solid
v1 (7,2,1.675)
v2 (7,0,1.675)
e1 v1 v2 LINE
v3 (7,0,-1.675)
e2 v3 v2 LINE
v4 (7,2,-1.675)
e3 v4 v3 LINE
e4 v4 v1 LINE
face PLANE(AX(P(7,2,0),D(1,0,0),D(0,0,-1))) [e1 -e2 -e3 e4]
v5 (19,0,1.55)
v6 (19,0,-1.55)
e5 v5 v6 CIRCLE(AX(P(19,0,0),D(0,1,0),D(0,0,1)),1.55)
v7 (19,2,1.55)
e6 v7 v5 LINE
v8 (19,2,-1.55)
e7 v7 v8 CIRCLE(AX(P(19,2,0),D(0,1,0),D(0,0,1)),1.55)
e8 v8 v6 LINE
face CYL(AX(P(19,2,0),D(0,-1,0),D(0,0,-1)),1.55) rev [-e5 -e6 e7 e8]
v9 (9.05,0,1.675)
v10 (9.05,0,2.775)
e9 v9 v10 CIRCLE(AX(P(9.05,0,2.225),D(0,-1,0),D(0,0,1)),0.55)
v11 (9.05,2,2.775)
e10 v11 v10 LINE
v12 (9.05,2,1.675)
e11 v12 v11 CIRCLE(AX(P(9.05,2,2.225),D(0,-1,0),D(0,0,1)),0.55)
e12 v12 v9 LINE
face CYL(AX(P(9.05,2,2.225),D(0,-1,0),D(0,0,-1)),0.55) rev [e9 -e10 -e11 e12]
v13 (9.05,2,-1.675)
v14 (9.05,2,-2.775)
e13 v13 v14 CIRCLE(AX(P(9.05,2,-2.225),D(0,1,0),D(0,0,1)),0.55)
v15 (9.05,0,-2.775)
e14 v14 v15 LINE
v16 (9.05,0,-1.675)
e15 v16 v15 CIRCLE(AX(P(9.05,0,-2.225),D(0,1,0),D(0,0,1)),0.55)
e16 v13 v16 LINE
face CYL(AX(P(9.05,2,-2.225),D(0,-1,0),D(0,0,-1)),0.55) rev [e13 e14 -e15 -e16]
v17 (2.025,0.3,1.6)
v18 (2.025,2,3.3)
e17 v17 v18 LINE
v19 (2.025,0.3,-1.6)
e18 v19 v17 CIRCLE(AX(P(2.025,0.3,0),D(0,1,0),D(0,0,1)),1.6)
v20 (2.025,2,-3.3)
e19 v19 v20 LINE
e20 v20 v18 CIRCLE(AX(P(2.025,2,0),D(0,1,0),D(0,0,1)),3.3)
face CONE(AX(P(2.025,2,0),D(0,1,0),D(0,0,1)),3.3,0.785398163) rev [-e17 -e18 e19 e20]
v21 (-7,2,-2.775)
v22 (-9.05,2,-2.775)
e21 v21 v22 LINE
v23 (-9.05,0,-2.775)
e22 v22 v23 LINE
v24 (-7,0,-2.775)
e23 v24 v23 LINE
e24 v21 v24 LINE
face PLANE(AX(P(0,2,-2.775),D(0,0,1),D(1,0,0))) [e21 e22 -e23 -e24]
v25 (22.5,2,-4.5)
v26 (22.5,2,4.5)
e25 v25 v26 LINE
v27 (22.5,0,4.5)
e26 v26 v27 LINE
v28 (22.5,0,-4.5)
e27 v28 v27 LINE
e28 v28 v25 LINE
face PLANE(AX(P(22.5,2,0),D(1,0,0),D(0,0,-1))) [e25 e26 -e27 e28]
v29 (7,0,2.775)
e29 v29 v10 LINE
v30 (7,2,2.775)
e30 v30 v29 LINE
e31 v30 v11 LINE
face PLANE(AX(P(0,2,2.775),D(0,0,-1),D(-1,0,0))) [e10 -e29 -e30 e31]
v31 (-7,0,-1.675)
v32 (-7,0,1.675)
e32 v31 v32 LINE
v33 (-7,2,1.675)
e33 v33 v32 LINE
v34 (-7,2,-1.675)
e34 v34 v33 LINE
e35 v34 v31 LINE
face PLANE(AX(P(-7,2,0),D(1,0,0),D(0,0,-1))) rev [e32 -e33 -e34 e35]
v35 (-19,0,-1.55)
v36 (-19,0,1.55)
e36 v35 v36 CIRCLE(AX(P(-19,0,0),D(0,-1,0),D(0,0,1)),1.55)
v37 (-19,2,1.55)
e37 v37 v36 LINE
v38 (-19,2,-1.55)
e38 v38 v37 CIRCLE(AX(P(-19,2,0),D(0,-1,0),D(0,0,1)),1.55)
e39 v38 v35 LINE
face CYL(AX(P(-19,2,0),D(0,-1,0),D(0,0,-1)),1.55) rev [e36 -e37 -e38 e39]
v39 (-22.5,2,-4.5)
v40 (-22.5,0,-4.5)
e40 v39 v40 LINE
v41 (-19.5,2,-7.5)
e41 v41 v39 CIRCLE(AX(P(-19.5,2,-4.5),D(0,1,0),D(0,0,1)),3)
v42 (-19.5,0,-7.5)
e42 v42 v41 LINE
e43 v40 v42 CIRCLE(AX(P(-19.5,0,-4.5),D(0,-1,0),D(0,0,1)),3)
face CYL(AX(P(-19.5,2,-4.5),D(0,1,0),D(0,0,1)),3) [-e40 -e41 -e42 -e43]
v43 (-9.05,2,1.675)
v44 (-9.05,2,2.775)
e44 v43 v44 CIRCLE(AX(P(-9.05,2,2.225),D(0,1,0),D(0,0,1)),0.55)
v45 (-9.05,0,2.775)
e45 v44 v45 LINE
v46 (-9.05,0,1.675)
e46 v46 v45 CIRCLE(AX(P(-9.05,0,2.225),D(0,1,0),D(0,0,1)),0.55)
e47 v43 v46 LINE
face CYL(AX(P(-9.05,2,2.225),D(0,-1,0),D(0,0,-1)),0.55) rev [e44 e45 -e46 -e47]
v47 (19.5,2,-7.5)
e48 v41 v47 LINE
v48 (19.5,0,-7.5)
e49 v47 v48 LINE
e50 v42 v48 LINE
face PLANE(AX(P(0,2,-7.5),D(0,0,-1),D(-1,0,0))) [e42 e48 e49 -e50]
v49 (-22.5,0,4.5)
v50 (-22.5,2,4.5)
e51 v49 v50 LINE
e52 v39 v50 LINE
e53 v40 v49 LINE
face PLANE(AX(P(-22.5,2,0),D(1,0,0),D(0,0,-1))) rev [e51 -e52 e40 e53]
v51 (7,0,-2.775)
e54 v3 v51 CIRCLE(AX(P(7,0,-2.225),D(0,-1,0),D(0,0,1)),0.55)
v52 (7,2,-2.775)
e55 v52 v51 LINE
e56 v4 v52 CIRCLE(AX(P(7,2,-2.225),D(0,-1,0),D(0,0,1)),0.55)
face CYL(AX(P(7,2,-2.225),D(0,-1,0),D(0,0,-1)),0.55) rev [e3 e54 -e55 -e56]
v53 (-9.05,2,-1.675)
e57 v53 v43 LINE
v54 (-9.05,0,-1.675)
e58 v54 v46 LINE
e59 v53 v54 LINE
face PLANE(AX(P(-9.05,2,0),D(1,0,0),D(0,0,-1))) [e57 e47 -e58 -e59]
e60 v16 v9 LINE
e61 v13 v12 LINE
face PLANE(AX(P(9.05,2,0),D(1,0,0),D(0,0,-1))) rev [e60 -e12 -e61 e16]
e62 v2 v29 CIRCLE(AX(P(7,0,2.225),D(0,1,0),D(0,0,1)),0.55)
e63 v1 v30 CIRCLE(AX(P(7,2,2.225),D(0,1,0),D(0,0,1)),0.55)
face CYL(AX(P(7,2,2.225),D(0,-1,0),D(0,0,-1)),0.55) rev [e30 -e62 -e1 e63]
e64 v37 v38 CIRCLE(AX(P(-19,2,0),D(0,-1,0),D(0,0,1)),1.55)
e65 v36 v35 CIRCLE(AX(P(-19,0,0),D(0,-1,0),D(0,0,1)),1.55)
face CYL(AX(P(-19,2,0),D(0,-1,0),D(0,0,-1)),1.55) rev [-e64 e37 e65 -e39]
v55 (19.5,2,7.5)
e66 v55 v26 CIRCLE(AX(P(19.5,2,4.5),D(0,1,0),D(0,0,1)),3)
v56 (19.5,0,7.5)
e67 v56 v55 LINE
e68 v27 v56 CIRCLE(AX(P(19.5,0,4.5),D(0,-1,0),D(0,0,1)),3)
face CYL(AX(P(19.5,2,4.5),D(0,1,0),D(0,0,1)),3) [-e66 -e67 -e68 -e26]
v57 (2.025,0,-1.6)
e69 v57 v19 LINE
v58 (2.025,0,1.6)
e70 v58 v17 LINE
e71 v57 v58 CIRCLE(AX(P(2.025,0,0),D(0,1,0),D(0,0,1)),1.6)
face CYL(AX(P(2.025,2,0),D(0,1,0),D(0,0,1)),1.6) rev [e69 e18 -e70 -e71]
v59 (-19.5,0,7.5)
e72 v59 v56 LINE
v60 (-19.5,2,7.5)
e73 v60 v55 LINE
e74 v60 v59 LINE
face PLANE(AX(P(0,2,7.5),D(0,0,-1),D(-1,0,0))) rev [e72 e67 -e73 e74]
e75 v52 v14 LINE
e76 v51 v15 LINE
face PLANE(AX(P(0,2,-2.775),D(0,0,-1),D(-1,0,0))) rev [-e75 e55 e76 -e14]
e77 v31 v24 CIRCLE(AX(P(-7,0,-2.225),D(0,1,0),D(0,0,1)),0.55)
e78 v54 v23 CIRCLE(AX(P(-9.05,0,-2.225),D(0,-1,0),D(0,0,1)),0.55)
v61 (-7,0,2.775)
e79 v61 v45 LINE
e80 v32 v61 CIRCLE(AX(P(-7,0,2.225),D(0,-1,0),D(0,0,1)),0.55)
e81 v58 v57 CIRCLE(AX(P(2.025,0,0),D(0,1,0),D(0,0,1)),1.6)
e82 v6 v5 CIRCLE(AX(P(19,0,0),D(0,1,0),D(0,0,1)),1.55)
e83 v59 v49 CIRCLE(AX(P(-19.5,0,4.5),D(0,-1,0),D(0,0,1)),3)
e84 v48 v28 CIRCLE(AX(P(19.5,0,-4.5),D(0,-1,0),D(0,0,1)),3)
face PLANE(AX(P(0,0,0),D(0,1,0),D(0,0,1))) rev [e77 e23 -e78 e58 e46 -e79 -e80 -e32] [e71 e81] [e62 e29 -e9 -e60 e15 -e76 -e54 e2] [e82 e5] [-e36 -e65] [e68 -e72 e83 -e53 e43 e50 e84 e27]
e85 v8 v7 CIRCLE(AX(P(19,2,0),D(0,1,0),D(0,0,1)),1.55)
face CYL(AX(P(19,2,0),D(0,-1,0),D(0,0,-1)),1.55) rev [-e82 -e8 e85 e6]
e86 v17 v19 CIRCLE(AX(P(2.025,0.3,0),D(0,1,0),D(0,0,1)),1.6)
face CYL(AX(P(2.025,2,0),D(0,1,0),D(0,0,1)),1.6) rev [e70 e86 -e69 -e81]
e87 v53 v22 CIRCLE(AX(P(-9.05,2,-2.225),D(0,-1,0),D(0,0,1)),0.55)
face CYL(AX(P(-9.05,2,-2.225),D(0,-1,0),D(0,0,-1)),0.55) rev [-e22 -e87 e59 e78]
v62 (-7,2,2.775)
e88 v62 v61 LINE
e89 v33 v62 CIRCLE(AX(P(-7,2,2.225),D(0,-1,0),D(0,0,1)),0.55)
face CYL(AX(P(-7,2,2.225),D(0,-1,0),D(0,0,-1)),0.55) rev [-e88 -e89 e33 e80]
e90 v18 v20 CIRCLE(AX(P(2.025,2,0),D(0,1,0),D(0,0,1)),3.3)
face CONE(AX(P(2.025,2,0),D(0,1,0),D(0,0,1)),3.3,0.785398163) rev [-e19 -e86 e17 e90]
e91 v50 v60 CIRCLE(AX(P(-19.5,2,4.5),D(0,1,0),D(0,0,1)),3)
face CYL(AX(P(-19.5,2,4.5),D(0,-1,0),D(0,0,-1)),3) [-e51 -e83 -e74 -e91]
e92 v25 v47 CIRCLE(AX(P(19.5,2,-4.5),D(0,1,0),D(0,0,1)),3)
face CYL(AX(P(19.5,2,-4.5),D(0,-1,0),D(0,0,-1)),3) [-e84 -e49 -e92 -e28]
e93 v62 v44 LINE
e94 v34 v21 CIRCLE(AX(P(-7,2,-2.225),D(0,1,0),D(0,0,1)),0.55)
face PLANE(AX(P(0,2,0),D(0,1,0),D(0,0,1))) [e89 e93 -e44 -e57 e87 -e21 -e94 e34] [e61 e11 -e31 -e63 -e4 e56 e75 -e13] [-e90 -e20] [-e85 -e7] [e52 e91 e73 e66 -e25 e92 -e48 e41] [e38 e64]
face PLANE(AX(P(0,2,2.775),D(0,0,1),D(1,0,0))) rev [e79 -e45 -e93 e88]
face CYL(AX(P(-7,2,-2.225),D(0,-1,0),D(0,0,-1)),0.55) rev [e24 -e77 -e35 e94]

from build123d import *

# Parameters (mm, degrees)
SKETCH_1_W                   = 45
SKETCH_1_H                   = 15
SKETCH_1_R                   = 1.55
EXTRUDE_1_DEPTH              = 2
FILLET_1_R                   = 3
HOLE_WIZARD_M3_1_D           = 3.2
HOLE_WIZARD_M3_1_DEPTH       = 7.5
HOLE_WIZARD_M3_1_CSINK_D     = 6.6
HOLE_WIZARD_M3_1_CSINK_ANGLE = 90
HOLE_WIZARD_M3_1_TIP         = 0.96137699


with BuildPart() as part:
    # 草图1 → 凸台-拉伸1 (new body)
    with BuildSketch(Plane(origin=(0, 0, 0), x_dir=(1, 0, 0), z_dir=(0, 1, 0))):
        Rectangle(SKETCH_1_W, SKETCH_1_H)
        with Locations(Location((-19, 0, 0), (0, 0, 270))):
            Circle(SKETCH_1_R, mode=Mode.SUBTRACT)
        with BuildLine():
            ThreePointArc((-9.05, 1.675), (-9.6, 2.225), (-9.05, 2.775))
            Line((-9.05, 2.775), (-7, 2.775))
            ThreePointArc((-7, 2.775), (-6.61109127, 2.61390873), (-6.45, 2.225))
            ThreePointArc((-6.45, 2.225), (-6.61109127, 1.83609127), (-7, 1.675))
            Line((-7, 1.675), (-7, -1.675))
            ThreePointArc((-7, -1.675), (-6.61109127, -1.83609127), (-6.45, -2.225))
            ThreePointArc((-6.45, -2.225), (-6.61109127, -2.61390873), (-7, -2.775))
            Line((-7, -2.775), (-9.05, -2.775))
            ThreePointArc((-9.05, -2.775), (-9.6, -2.225), (-9.05, -1.675))
            Line((-9.05, -1.675), (-9.05, 1.675))
        make_face(mode=Mode.SUBTRACT)
        with Locations(Location((2.025, 0, 0), (0, 0, 270))):
            Circle(SKETCH_1_R, mode=Mode.SUBTRACT)
        with BuildLine():
            ThreePointArc((7, 1.675), (6.45, 2.225), (7, 2.775))
            Line((7, 2.775), (9.05, 2.775))
            ThreePointArc((9.05, 2.775), (9.43890873, 2.61390873), (9.6, 2.225))
            ThreePointArc((9.6, 2.225), (9.43890873, 1.83609127), (9.05, 1.675))
            Line((9.05, 1.675), (9.05, -1.675))
            ThreePointArc((9.05, -1.675), (9.43890873, -1.83609127), (9.6, -2.225))
            ThreePointArc((9.6, -2.225), (9.43890873, -2.61390873), (9.05, -2.775))
            Line((9.05, -2.775), (7, -2.775))
            ThreePointArc((7, -2.775), (6.45, -2.225), (7, -1.675))
            Line((7, -1.675), (7, 1.675))
        make_face(mode=Mode.SUBTRACT)
        with Locations(Location((19, 0, 0), (0, 0, 270))):
            Circle(SKETCH_1_R, mode=Mode.SUBTRACT)
    extrude(amount=EXTRUDE_1_DEPTH)

    # 圆角1
    fillet_1_edges = [part.edges().sort_by_distance(p)[0] for p in [
        (22.5, 1, 7.5),
        (-22.5, 1, 7.5),
        (-22.5, 1, -7.5),
        (22.5, 1, -7.5),
    ]]
    fillet(fillet_1_edges, radius=FILLET_1_R)

    # M3 十字槽半沉头木螺钉的锥形沉头孔1
    with Locations(Plane(origin=(0, 2, 0), x_dir=(1, 0, 0), z_dir=(0, 1, 0))):
        with Locations((2.025, 0)):
            CounterSinkHole(HOLE_WIZARD_M3_1_D / 2, HOLE_WIZARD_M3_1_CSINK_D / 2, depth=HOLE_WIZARD_M3_1_DEPTH, counter_sink_angle=HOLE_WIZARD_M3_1_CSINK_ANGLE)
            with Locations((0, 0, -(HOLE_WIZARD_M3_1_DEPTH + HOLE_WIZARD_M3_1_TIP / 2))):  # 118° drill point
                Cone(0, HOLE_WIZARD_M3_1_D / 2, HOLE_WIZARD_M3_1_TIP, mode=Mode.SUBTRACT)


solid = part.part
